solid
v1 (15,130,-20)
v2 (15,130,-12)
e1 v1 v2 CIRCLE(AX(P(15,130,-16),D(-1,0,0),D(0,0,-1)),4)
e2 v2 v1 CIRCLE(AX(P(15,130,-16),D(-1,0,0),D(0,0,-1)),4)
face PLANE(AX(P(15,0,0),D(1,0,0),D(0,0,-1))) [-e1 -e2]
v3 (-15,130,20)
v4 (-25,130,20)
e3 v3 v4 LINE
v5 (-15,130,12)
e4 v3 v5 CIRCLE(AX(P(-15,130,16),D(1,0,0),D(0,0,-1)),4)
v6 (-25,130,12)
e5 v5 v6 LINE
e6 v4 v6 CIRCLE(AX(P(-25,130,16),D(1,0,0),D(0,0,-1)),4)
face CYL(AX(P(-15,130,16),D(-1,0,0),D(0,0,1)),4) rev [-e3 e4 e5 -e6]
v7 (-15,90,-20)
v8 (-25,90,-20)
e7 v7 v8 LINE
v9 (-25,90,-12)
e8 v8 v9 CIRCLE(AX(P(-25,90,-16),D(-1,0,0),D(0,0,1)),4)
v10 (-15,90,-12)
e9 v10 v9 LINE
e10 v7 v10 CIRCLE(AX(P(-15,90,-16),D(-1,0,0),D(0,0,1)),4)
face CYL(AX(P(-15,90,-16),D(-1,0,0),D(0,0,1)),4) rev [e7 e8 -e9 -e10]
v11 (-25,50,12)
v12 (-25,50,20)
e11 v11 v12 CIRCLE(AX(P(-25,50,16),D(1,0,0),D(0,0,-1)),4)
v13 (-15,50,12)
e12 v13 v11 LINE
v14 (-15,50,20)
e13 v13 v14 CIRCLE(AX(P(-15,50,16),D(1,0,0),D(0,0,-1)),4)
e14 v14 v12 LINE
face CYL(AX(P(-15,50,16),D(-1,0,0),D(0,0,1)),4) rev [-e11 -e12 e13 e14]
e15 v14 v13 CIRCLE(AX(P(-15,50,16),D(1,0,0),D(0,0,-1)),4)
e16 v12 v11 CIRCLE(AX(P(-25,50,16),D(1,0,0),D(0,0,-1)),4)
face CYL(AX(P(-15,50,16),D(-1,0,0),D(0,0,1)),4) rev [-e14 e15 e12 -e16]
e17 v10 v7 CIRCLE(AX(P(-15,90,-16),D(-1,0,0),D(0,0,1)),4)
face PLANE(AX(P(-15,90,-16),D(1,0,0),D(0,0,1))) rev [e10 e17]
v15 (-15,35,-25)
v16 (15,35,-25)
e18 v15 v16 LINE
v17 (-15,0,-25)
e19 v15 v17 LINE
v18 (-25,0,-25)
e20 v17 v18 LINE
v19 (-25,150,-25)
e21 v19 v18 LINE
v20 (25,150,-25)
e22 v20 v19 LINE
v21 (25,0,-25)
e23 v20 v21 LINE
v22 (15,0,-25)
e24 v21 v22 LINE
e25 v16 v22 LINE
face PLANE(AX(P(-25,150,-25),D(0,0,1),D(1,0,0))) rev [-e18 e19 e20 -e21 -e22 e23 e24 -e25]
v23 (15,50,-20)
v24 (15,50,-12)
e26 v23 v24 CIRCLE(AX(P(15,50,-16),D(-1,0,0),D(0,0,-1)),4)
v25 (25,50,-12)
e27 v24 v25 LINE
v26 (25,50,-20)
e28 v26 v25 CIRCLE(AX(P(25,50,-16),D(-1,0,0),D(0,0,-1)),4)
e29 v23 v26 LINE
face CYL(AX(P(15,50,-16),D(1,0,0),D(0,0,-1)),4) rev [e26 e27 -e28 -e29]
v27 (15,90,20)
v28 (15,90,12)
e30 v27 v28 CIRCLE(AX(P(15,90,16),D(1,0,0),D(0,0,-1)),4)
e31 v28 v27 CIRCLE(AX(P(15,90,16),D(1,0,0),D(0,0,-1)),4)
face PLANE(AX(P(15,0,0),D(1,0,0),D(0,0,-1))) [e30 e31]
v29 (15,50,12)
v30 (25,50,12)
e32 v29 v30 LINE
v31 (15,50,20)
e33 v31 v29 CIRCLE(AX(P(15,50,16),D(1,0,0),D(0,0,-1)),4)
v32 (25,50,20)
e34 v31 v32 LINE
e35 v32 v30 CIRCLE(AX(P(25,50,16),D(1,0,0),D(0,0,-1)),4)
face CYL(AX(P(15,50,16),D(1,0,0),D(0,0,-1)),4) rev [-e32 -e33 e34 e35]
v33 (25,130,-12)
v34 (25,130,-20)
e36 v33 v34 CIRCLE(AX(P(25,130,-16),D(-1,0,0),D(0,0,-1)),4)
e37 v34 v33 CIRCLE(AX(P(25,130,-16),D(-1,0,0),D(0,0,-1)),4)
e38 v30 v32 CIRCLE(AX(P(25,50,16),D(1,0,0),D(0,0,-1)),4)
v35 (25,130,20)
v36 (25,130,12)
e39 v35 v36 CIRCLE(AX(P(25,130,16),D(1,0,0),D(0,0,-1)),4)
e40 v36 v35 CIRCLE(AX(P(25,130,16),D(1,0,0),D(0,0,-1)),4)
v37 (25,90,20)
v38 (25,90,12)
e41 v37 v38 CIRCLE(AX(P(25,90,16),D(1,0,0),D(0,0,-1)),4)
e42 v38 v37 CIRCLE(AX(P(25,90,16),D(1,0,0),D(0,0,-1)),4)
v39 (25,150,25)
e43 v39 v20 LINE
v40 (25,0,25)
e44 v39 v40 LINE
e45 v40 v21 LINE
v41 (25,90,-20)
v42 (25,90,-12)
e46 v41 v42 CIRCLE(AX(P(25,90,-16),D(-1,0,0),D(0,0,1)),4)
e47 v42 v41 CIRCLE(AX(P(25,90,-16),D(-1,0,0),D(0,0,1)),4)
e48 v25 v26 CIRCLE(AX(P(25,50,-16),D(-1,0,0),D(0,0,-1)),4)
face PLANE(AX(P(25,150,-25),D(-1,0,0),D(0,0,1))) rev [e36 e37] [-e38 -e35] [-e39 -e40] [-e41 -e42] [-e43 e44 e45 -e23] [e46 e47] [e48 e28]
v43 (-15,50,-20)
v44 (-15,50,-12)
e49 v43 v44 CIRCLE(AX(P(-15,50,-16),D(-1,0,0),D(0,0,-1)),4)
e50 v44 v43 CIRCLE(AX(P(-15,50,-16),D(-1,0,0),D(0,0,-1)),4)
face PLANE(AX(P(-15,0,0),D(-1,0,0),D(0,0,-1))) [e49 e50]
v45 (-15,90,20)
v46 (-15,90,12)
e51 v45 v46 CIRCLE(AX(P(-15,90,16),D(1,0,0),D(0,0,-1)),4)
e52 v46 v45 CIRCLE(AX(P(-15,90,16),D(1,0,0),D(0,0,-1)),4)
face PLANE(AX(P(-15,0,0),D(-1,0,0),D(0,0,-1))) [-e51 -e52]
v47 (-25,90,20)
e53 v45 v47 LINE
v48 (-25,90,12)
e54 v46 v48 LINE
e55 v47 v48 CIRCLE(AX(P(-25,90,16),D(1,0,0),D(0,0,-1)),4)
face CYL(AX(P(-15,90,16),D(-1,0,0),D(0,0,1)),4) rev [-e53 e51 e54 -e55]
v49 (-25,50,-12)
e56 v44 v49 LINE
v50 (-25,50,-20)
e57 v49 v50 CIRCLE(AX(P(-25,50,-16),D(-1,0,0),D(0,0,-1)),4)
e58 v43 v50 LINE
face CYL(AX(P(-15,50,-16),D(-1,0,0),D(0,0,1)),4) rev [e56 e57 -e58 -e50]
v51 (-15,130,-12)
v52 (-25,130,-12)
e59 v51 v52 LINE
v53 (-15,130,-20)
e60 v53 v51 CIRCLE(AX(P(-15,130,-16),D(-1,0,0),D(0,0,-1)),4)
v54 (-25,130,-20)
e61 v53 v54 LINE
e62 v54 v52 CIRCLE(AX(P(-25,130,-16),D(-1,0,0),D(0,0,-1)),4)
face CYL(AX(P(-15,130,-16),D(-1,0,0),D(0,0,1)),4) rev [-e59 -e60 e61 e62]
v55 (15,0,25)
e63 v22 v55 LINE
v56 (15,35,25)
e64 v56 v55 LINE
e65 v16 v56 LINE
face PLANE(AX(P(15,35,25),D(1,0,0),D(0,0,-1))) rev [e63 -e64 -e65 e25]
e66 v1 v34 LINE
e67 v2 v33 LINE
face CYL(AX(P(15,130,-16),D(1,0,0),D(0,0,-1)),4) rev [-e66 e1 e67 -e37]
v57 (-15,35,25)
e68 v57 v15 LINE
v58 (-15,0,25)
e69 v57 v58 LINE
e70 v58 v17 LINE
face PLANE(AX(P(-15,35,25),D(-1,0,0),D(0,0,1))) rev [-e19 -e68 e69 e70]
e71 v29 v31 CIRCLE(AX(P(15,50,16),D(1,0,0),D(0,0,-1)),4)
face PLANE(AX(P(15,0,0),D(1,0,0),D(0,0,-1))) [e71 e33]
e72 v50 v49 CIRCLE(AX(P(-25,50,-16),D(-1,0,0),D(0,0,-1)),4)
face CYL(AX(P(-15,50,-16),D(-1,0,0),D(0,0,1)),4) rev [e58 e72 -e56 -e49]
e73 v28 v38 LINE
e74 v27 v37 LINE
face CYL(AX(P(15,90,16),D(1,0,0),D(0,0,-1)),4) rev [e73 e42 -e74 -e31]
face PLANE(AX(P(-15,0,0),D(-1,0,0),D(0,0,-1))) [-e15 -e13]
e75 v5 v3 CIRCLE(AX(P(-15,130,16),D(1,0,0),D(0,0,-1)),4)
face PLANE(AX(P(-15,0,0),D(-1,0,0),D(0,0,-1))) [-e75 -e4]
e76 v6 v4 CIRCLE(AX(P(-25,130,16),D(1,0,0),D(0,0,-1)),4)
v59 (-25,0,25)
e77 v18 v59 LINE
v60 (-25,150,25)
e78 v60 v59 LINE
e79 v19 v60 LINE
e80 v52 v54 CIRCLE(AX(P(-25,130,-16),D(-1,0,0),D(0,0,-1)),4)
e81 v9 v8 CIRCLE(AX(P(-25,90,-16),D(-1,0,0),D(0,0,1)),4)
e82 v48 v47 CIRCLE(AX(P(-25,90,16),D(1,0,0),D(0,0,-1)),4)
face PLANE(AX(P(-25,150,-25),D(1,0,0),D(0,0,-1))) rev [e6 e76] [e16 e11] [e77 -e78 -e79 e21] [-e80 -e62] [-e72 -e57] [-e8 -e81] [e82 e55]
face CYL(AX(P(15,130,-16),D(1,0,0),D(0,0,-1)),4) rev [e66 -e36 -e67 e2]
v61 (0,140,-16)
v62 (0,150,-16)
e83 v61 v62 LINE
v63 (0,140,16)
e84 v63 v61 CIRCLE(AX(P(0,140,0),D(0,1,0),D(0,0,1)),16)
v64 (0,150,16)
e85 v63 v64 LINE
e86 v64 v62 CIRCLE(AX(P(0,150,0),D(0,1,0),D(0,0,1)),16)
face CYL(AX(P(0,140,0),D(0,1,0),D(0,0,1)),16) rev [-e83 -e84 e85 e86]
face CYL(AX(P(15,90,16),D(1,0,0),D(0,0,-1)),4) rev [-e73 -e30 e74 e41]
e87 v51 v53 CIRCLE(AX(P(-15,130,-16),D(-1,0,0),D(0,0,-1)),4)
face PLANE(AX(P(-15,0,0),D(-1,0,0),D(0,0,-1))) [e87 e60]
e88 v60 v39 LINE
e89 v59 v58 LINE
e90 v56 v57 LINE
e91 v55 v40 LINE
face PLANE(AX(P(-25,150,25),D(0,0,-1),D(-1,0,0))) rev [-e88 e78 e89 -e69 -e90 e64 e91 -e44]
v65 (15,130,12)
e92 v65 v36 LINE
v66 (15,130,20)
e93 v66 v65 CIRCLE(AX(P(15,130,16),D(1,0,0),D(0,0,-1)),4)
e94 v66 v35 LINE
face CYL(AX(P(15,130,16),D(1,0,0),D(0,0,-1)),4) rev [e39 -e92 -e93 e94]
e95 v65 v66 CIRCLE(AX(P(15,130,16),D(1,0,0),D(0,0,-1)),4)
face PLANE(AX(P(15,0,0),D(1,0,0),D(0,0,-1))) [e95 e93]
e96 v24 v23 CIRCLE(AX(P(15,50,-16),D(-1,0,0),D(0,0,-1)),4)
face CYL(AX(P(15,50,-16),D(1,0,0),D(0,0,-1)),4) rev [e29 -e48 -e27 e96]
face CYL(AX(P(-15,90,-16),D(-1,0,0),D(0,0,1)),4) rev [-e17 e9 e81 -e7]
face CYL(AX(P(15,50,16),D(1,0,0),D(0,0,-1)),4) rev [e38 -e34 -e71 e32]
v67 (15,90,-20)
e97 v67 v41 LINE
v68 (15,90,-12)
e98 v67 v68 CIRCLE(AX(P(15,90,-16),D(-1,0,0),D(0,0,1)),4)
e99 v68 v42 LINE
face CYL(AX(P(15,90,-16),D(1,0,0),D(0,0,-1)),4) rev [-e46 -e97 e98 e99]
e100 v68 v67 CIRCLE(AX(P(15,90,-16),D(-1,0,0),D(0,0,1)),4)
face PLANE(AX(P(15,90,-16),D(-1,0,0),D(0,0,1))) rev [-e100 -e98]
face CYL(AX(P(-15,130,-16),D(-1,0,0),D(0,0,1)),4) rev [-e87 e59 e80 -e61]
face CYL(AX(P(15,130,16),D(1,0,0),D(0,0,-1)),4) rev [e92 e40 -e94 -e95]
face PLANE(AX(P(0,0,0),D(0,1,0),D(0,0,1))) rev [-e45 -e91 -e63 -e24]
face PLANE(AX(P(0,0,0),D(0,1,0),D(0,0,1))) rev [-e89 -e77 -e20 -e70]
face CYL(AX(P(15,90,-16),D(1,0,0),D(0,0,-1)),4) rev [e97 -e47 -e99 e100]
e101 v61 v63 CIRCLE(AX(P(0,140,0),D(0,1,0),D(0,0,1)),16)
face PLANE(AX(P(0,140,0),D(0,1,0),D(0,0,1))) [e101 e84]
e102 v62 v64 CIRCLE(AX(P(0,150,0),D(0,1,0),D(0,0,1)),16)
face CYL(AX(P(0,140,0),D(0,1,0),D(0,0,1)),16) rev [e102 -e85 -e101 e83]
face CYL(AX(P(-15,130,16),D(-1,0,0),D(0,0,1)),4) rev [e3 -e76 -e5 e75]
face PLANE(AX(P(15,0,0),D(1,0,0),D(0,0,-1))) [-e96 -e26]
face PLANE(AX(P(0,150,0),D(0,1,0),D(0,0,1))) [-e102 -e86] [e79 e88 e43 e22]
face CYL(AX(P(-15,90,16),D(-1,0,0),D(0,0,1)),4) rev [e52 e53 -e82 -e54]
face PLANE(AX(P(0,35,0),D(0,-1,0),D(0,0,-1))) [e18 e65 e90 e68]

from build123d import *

# Parameters (mm, degrees)
SKETCH1_W           = 50
SKETCH1_H           = 50
BOSS_EXTRUDE2_DEPTH = 150
SKETCH2_W           = 30
SKETCH2_H           = 50
CUT_EXTRUDE1_DEPTH  = 35
SKETCH4_R           = 16
CUT_EXTRUDE2_DEPTH  = 10
SKETCH5_R           = 4
CUT_EXTRUDE3_DEPTH  = 10


with BuildPart() as part:
    # Sketch1 → Boss-Extrude2 (new body)
    with BuildSketch(Plane(origin=(0, 0, 0), x_dir=(1, 0, 0), z_dir=(0, 1, 0))):
        Rectangle(SKETCH1_W, SKETCH1_H)
    extrude(amount=BOSS_EXTRUDE2_DEPTH)

    # Sketch2 → Cut-Extrude1 (cut)
    with BuildSketch(Plane.XZ):
        Rectangle(SKETCH2_W, SKETCH2_H)
    extrude(amount=-CUT_EXTRUDE1_DEPTH, mode=Mode.SUBTRACT)

    # Sketch4 → Cut-Extrude2 (cut)
    with BuildSketch(Plane(origin=(0, 150, 0), x_dir=(1, 0, 0), z_dir=(0, 1, 0))):
        with Locations(Location((0, 0, 0), (0, 0, 270))):
            Circle(SKETCH4_R)
    extrude(amount=-CUT_EXTRUDE2_DEPTH, mode=Mode.SUBTRACT)

    # Sketch5 → Cut-Extrude3 (cut)
    with BuildSketch(Plane(origin=(25, 0, 0), x_dir=(0, 0, -1), z_dir=(1, 0, 0))):
        with Locations((-16, 130)):
            Circle(SKETCH5_R)
        with Locations((16, 130)):
            Circle(SKETCH5_R)
        with Locations((-16, 90)):
            Circle(SKETCH5_R)
        with Locations((-16, 50)):
            Circle(SKETCH5_R)
        with Locations((16, 50)):
            Circle(SKETCH5_R)
        with Locations(Location((16, 90, 0), (0, 0, 180))):
            Circle(SKETCH5_R)
    cut_extrude3 = extrude(amount=-CUT_EXTRUDE3_DEPTH, mode=Mode.SUBTRACT)

    # Mirror1: Cut-Extrude3 across plane
    add(cut_extrude3.mirror(Plane(origin=(0, 0, 0), x_dir=(0, 0, 1), z_dir=(1, 0, 0))), mode=Mode.SUBTRACT)


solid = part.part
